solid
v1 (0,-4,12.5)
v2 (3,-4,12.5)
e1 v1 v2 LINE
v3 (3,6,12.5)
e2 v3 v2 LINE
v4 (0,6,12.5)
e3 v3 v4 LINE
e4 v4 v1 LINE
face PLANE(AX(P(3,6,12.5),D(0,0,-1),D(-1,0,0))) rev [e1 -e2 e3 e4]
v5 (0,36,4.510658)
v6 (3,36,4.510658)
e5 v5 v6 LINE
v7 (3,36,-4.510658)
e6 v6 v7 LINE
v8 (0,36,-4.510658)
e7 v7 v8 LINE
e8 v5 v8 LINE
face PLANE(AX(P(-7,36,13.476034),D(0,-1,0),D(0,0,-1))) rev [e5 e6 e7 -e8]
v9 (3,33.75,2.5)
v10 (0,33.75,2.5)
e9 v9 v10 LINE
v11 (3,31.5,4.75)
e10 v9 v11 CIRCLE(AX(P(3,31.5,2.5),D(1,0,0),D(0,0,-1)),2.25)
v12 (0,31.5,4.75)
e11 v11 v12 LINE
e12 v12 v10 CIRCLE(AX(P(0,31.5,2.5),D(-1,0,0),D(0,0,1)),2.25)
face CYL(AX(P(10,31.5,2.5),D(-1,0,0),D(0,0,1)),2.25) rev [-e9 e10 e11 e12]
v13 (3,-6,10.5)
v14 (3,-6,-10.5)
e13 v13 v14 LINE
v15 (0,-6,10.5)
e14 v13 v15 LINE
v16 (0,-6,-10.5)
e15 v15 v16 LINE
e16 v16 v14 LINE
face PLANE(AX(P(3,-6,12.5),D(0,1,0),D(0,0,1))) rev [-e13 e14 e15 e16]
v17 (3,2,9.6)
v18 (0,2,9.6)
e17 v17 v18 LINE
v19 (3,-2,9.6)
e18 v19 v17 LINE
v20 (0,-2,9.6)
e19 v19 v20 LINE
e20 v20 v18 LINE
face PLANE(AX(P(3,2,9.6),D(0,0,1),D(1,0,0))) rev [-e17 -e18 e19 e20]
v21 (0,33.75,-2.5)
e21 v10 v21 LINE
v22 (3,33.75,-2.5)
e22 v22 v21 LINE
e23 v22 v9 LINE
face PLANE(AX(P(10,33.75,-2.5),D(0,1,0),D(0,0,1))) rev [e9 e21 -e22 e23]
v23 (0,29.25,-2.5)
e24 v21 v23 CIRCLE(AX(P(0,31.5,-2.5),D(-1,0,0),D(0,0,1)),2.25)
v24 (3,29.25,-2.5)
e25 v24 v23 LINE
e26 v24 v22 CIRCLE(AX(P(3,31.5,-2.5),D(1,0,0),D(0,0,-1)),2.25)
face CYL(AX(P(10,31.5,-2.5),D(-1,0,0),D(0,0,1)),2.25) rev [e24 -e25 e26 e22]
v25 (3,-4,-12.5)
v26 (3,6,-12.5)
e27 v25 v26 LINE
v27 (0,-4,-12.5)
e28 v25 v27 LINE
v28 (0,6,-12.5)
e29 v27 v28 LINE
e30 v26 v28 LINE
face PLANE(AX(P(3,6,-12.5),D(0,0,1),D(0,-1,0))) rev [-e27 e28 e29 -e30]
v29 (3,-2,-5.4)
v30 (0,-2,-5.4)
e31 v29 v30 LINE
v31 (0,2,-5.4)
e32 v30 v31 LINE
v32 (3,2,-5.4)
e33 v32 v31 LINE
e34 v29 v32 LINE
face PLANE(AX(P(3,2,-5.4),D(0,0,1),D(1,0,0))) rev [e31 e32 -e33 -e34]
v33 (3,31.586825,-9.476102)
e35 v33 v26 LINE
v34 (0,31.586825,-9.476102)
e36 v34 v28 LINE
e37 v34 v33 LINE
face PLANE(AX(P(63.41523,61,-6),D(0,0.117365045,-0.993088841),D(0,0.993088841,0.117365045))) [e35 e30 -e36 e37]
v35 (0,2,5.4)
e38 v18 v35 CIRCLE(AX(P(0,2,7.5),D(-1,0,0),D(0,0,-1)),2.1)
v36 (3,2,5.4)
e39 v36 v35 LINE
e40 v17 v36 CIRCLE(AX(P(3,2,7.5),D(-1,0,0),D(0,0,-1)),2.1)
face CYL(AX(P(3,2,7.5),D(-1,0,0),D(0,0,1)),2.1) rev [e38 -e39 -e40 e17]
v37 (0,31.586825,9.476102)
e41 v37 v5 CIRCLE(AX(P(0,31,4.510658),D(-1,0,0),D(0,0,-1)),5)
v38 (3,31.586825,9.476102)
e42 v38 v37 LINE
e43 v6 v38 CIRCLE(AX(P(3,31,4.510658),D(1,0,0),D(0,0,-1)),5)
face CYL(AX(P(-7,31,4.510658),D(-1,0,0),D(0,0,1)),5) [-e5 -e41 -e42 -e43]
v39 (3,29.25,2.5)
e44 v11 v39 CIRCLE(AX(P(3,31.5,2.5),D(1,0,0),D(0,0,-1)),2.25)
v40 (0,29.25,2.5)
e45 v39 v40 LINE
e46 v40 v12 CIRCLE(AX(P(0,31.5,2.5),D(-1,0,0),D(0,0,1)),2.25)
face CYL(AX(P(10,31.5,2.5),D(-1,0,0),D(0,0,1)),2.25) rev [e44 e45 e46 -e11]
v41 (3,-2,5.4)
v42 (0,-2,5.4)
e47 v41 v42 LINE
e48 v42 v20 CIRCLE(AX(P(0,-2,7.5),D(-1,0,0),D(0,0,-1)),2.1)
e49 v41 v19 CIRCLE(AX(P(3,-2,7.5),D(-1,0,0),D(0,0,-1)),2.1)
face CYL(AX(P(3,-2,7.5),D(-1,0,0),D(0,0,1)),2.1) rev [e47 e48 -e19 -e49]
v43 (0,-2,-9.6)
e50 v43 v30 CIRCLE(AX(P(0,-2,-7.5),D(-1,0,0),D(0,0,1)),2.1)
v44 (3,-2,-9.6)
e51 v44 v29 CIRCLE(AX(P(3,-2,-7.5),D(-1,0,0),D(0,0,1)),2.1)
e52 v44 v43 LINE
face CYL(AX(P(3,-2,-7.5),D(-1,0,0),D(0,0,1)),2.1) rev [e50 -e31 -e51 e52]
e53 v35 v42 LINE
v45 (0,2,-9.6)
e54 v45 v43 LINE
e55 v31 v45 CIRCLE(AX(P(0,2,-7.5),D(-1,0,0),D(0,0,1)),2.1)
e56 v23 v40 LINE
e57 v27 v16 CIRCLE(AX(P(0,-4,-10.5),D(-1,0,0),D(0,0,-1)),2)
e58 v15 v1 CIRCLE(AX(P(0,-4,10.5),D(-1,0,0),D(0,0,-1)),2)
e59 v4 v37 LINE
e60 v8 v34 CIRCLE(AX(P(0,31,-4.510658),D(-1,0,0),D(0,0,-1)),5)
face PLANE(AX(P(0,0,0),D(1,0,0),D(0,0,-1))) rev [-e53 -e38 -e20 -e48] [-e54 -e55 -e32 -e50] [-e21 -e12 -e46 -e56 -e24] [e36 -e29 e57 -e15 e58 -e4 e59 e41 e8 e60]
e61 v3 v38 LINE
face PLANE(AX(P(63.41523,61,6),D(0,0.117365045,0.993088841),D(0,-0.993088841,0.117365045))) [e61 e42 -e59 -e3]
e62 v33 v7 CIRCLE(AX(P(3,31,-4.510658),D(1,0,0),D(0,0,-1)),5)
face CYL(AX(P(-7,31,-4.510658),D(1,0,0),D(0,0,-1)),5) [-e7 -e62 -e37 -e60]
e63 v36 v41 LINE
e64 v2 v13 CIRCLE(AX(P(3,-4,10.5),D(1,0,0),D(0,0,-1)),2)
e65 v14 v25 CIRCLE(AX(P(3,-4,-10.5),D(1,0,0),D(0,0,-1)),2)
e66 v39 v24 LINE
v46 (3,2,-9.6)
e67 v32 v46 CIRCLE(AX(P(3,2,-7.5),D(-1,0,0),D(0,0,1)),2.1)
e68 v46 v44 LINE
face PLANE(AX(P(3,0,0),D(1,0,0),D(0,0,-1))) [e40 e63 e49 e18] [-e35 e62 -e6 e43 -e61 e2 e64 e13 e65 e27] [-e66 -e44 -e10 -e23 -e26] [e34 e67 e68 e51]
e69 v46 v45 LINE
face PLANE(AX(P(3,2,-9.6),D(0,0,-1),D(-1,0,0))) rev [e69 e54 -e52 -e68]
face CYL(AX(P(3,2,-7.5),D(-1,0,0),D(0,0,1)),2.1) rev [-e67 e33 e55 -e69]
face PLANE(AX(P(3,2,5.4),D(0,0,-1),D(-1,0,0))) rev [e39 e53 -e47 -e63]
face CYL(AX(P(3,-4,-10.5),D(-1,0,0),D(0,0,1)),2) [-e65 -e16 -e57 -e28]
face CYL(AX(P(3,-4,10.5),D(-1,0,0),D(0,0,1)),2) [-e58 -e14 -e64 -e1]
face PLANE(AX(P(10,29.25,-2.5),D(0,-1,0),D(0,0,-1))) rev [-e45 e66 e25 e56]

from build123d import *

# Parameters (mm, degrees)
EXTRUDE_1_DEPTH             = 3
EXTRUDE_2_DEPTH             = 3
FILLET_1_R                  = 2
CUT_EXTRUDE_1_DEPTH         = 3
FILLET_2_R                  = 2
HOLE_WIZARD_4_3_4_3_1_D     = 4.3
HOLE_WIZARD_4_3_4_3_1_DEPTH = 10.1
HOLE_WIZARD_4_3_4_3_1_TIP   = 1.291850331
SKETCH_7_W                  = 24.449376322
SKETCH_7_H                  = 27.885292322
CUT_EXTRUDE_2_DEPTH         = 10
CUT_EXTRUDE_3_DEPTH         = 10
FILLET_3_R                  = 5


with BuildPart() as part:
    # 草图1 → 凸台-拉伸1 (new body)
    with BuildSketch(Plane(origin=(0, 0, 0), x_dir=(0, 0, -1), z_dir=(1, 0, 0))):
        Polygon((-12.5, 6), (-6, 6), (-6, 61), (6, 61), (6, 6), (12.5, 6), (12.5, -6), (-12.5, -6), align=None)
    extrude(amount=EXTRUDE_1_DEPTH)

    # 草图2 → 凸台-拉伸2 (add)
    with BuildSketch(Plane.ZY):
        Polygon((-6, 61), (-12.5, 6), (12.5, 6), (6, 61), align=None)
    extrude(amount=-EXTRUDE_2_DEPTH)

    # 圆角1
    fillet_1_edges = [part.edges().sort_by_distance(p)[0] for p in [
        (1.5, 61, 6),
        (1.5, 61, -6),
    ]]
    fillet(fillet_1_edges, radius=FILLET_1_R)

    # 草图3 → 切除-拉伸1 (cut)
    with BuildSketch(Plane.ZY):
        with BuildLine():
            Line((-5.4, 2), (-5.4, -2))
            ThreePointArc((-5.4, -2), (-7.5, -4.1), (-9.6, -2))
            Line((-9.6, -2), (-9.6, 2))
            ThreePointArc((-9.6, 2), (-7.5, 4.1), (-5.4, 2))
        make_face()
        with BuildLine():
            Line((5.4, 2), (5.4, -2))
            ThreePointArc((5.4, -2), (7.5, -4.1), (9.6, -2))
            Line((9.6, -2), (9.6, 2))
            ThreePointArc((9.6, 2), (7.5, 4.1), (5.4, 2))
        make_face()
    extrude(amount=-CUT_EXTRUDE_1_DEPTH, mode=Mode.SUBTRACT)

    # 圆角2
    fillet_2_edges = [part.edges().sort_by_distance(p)[0] for p in [
        (1.5, -6, -12.5),
        (1.5, -6, 12.5),
    ]]
    fillet(fillet_2_edges, radius=FILLET_2_R)

    # Ø4.3 (4.3) 直径孔1
    with Locations(Plane.ZY):
        with Locations((0, 56), (0, 41)):
            Hole(HOLE_WIZARD_4_3_4_3_1_D / 2, depth=HOLE_WIZARD_4_3_4_3_1_DEPTH)
            with Locations((0, 0, -(HOLE_WIZARD_4_3_4_3_1_DEPTH + HOLE_WIZARD_4_3_4_3_1_TIP / 2))):  # 118° drill point
                Cone(0, HOLE_WIZARD_4_3_4_3_1_D / 2, HOLE_WIZARD_4_3_4_3_1_TIP, mode=Mode.SUBTRACT)

    # 草图7 → 切除-拉伸2 (cut)
    with BuildSketch(Plane(origin=(3, 0, 0), x_dir=(0, 0, -1), z_dir=(1, 0, 0))):
        with Locations((-1.251346032, 49.942646161)):
            Rectangle(SKETCH_7_W, SKETCH_7_H)
    extrude(amount=-CUT_EXTRUDE_2_DEPTH, mode=Mode.SUBTRACT)

    # 草图8 → 切除-拉伸3 (cut)
    with BuildSketch(Plane.ZY):
        with BuildLine():
            Line((-2.5, 33.75), (2.5, 33.75))
            ThreePointArc((2.5, 33.75), (4.75, 31.5), (2.5, 29.25))
            Line((2.5, 29.25), (-2.5, 29.25))
            ThreePointArc((-2.5, 29.25), (-4.75, 31.5), (-2.5, 33.75))
        make_face()
    extrude(amount=-CUT_EXTRUDE_3_DEPTH, mode=Mode.SUBTRACT)

    # 圆角3
    fillet_3_edges = [part.edges().sort_by_distance(p)[0] for p in [
        (1.5, 36, 8.954545455),
        (1.5, 36, -8.954545455),
    ]]
    fillet(fillet_3_edges, radius=FILLET_3_R)


solid = part.part
